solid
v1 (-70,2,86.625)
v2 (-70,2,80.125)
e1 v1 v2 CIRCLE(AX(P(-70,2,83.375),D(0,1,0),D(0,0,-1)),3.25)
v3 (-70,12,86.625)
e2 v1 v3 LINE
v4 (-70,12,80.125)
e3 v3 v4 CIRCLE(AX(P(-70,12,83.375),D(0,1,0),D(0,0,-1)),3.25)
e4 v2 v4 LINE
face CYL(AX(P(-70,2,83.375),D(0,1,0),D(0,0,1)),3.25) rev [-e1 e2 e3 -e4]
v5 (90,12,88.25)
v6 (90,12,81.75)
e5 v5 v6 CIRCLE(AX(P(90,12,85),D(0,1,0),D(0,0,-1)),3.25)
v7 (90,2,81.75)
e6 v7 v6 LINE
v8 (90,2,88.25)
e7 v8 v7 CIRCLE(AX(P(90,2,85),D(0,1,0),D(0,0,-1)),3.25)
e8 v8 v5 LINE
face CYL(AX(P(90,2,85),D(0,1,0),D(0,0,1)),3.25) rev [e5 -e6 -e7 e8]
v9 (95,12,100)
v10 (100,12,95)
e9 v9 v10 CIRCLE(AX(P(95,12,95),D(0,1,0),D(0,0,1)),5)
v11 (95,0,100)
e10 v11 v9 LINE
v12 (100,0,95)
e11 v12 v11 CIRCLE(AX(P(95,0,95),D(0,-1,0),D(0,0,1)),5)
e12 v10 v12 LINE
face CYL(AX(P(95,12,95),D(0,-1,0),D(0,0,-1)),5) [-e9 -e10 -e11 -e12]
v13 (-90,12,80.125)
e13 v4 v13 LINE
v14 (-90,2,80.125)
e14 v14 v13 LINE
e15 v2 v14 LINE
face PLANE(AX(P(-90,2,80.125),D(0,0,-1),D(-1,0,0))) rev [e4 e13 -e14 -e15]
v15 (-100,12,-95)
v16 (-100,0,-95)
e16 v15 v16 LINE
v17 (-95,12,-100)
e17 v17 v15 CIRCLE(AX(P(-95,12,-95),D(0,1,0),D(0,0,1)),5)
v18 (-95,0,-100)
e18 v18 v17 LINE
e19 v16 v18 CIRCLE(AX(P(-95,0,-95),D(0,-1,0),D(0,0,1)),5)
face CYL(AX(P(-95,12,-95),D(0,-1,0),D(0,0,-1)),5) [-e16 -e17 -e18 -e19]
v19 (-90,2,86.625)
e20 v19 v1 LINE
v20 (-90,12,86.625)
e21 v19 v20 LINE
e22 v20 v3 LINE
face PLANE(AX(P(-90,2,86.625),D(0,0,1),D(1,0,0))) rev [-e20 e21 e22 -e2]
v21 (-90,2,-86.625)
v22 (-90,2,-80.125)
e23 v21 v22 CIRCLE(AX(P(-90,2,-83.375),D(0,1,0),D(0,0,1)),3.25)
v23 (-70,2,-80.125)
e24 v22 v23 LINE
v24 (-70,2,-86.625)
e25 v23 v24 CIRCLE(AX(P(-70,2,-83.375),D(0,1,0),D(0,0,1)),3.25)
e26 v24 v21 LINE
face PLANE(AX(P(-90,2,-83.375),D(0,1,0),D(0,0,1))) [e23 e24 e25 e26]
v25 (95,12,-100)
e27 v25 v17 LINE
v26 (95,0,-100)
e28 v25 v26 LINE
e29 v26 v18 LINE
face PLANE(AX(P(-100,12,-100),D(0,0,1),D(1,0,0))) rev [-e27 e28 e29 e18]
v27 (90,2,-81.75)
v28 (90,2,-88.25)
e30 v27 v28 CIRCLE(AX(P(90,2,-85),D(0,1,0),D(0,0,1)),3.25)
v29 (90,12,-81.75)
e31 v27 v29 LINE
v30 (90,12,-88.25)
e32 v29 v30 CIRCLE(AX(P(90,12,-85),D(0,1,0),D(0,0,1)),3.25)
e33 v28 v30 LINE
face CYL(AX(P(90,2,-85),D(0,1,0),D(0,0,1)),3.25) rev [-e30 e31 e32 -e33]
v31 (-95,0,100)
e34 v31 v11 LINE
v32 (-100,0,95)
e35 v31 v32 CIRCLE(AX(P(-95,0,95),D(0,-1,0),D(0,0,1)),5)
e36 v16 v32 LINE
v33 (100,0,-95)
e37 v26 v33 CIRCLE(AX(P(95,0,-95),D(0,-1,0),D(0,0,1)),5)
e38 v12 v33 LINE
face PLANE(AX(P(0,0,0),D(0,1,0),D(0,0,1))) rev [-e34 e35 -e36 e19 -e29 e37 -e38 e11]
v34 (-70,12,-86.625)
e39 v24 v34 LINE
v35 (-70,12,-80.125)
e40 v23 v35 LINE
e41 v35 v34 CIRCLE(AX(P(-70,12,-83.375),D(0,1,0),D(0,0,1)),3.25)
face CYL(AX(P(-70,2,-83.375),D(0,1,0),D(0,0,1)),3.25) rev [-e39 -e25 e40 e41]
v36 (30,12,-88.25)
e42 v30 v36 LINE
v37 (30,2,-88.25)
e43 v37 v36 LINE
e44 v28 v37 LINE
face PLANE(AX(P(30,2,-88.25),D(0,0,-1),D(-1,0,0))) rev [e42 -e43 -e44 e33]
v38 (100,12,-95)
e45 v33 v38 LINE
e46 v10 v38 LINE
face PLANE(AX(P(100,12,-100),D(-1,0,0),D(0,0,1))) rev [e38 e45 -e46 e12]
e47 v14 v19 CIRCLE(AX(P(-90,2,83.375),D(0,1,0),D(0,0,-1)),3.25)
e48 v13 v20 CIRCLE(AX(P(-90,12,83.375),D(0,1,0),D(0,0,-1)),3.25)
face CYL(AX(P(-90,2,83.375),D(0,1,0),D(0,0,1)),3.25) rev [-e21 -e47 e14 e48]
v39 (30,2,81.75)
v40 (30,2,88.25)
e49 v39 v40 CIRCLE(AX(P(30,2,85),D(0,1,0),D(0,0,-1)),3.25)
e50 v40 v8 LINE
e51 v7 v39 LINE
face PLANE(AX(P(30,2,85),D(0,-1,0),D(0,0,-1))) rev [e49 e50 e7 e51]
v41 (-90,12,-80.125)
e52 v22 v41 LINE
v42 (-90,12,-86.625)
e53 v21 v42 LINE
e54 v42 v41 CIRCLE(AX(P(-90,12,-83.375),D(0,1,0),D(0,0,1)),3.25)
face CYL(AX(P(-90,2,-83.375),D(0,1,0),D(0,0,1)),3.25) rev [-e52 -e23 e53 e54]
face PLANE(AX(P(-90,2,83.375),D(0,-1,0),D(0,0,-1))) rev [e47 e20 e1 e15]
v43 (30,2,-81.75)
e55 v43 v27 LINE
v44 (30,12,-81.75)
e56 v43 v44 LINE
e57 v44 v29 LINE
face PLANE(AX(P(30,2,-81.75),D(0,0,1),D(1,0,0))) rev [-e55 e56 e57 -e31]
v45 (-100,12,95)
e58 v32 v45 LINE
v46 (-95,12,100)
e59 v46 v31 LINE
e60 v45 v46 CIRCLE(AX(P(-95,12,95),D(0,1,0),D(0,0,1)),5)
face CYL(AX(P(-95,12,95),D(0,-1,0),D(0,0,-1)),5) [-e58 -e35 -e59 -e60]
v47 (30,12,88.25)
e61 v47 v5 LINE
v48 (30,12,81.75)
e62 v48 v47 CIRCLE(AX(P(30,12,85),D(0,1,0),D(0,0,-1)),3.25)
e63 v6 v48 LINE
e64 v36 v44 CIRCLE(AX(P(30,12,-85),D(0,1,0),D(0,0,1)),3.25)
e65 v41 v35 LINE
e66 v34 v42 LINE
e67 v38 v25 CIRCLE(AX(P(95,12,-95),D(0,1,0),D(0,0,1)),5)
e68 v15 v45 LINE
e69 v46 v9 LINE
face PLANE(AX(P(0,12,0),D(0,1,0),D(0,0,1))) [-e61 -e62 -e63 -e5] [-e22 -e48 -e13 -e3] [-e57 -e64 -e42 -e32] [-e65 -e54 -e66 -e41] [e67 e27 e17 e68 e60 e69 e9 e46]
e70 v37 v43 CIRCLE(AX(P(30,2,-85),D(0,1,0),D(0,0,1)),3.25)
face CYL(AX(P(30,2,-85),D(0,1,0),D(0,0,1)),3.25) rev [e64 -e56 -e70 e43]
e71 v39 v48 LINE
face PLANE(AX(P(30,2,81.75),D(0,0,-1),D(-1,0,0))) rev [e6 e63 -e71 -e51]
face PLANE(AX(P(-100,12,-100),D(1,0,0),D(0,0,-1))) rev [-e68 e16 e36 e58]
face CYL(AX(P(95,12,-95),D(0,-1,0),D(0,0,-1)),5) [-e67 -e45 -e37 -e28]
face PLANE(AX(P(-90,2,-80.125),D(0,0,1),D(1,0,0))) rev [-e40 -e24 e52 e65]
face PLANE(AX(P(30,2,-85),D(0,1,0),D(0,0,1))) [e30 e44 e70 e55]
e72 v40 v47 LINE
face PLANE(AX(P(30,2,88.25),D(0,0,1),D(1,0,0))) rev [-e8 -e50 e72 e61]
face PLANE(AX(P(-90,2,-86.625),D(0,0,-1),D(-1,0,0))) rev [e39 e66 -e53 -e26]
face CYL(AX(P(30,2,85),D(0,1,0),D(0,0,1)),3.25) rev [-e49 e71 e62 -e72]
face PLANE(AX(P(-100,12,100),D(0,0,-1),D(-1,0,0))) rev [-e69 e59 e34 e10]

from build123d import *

# Parameters (mm, degrees)
SKETCH_1_W          = 200
SKETCH_1_H          = 200
EXTRUDE_1_DEPTH     = 12
FILLET_1_R          = 5
CUT_EXTRUDE_1_DEPTH = 10


with BuildPart() as part:
    # 草图1 → 凸台-拉伸1 (new body)
    with BuildSketch(Plane(origin=(0, 0, 0), x_dir=(1, 0, 0), z_dir=(0, 1, 0))):
        Rectangle(SKETCH_1_W, SKETCH_1_H)
    extrude(amount=EXTRUDE_1_DEPTH)

    # 圆角1
    fillet_1_edges = [part.edges().sort_by_distance(p)[0] for p in [
        (100, 6, 100),
        (-100, 6, 100),
        (-100, 6, -100),
        (100, 6, -100),
    ]]
    fillet(fillet_1_edges, radius=FILLET_1_R)

    # 草图2 → 切除-拉伸1 (cut)
    with BuildSketch(Plane(origin=(0, 12, 0), x_dir=(1, 0, 0), z_dir=(0, 1, 0))):
        with BuildLine():
            Line((-90, 86.625), (-70, 86.625))
            ThreePointArc((-70, 86.625), (-66.75, 83.375), (-70, 80.125))
            Line((-70, 80.125), (-90, 80.125))
            ThreePointArc((-90, 80.125), (-93.25, 83.375), (-90, 86.625))
        make_face()
        with BuildLine():
            Line((-90, -86.625), (-70, -86.625))
            ThreePointArc((-70, -86.625), (-66.75, -83.375), (-70, -80.125))
            Line((-70, -80.125), (-90, -80.125))
            ThreePointArc((-90, -80.125), (-93.25, -83.375), (-90, -86.625))
        make_face()
        with BuildLine():
            Line((30, 88.25), (90, 88.25))
            ThreePointArc((90, 88.25), (93.25, 85), (90, 81.75))
            Line((90, 81.75), (30, 81.75))
            ThreePointArc((30, 81.75), (26.75, 85), (30, 88.25))
        make_face()
        with BuildLine():
            Line((30, -88.25), (90, -88.25))
            ThreePointArc((90, -88.25), (93.25, -85), (90, -81.75))
            Line((90, -81.75), (30, -81.75))
            ThreePointArc((30, -81.75), (26.75, -85), (30, -88.25))
        make_face()
    extrude(amount=-CUT_EXTRUDE_1_DEPTH, mode=Mode.SUBTRACT)


solid = part.part
